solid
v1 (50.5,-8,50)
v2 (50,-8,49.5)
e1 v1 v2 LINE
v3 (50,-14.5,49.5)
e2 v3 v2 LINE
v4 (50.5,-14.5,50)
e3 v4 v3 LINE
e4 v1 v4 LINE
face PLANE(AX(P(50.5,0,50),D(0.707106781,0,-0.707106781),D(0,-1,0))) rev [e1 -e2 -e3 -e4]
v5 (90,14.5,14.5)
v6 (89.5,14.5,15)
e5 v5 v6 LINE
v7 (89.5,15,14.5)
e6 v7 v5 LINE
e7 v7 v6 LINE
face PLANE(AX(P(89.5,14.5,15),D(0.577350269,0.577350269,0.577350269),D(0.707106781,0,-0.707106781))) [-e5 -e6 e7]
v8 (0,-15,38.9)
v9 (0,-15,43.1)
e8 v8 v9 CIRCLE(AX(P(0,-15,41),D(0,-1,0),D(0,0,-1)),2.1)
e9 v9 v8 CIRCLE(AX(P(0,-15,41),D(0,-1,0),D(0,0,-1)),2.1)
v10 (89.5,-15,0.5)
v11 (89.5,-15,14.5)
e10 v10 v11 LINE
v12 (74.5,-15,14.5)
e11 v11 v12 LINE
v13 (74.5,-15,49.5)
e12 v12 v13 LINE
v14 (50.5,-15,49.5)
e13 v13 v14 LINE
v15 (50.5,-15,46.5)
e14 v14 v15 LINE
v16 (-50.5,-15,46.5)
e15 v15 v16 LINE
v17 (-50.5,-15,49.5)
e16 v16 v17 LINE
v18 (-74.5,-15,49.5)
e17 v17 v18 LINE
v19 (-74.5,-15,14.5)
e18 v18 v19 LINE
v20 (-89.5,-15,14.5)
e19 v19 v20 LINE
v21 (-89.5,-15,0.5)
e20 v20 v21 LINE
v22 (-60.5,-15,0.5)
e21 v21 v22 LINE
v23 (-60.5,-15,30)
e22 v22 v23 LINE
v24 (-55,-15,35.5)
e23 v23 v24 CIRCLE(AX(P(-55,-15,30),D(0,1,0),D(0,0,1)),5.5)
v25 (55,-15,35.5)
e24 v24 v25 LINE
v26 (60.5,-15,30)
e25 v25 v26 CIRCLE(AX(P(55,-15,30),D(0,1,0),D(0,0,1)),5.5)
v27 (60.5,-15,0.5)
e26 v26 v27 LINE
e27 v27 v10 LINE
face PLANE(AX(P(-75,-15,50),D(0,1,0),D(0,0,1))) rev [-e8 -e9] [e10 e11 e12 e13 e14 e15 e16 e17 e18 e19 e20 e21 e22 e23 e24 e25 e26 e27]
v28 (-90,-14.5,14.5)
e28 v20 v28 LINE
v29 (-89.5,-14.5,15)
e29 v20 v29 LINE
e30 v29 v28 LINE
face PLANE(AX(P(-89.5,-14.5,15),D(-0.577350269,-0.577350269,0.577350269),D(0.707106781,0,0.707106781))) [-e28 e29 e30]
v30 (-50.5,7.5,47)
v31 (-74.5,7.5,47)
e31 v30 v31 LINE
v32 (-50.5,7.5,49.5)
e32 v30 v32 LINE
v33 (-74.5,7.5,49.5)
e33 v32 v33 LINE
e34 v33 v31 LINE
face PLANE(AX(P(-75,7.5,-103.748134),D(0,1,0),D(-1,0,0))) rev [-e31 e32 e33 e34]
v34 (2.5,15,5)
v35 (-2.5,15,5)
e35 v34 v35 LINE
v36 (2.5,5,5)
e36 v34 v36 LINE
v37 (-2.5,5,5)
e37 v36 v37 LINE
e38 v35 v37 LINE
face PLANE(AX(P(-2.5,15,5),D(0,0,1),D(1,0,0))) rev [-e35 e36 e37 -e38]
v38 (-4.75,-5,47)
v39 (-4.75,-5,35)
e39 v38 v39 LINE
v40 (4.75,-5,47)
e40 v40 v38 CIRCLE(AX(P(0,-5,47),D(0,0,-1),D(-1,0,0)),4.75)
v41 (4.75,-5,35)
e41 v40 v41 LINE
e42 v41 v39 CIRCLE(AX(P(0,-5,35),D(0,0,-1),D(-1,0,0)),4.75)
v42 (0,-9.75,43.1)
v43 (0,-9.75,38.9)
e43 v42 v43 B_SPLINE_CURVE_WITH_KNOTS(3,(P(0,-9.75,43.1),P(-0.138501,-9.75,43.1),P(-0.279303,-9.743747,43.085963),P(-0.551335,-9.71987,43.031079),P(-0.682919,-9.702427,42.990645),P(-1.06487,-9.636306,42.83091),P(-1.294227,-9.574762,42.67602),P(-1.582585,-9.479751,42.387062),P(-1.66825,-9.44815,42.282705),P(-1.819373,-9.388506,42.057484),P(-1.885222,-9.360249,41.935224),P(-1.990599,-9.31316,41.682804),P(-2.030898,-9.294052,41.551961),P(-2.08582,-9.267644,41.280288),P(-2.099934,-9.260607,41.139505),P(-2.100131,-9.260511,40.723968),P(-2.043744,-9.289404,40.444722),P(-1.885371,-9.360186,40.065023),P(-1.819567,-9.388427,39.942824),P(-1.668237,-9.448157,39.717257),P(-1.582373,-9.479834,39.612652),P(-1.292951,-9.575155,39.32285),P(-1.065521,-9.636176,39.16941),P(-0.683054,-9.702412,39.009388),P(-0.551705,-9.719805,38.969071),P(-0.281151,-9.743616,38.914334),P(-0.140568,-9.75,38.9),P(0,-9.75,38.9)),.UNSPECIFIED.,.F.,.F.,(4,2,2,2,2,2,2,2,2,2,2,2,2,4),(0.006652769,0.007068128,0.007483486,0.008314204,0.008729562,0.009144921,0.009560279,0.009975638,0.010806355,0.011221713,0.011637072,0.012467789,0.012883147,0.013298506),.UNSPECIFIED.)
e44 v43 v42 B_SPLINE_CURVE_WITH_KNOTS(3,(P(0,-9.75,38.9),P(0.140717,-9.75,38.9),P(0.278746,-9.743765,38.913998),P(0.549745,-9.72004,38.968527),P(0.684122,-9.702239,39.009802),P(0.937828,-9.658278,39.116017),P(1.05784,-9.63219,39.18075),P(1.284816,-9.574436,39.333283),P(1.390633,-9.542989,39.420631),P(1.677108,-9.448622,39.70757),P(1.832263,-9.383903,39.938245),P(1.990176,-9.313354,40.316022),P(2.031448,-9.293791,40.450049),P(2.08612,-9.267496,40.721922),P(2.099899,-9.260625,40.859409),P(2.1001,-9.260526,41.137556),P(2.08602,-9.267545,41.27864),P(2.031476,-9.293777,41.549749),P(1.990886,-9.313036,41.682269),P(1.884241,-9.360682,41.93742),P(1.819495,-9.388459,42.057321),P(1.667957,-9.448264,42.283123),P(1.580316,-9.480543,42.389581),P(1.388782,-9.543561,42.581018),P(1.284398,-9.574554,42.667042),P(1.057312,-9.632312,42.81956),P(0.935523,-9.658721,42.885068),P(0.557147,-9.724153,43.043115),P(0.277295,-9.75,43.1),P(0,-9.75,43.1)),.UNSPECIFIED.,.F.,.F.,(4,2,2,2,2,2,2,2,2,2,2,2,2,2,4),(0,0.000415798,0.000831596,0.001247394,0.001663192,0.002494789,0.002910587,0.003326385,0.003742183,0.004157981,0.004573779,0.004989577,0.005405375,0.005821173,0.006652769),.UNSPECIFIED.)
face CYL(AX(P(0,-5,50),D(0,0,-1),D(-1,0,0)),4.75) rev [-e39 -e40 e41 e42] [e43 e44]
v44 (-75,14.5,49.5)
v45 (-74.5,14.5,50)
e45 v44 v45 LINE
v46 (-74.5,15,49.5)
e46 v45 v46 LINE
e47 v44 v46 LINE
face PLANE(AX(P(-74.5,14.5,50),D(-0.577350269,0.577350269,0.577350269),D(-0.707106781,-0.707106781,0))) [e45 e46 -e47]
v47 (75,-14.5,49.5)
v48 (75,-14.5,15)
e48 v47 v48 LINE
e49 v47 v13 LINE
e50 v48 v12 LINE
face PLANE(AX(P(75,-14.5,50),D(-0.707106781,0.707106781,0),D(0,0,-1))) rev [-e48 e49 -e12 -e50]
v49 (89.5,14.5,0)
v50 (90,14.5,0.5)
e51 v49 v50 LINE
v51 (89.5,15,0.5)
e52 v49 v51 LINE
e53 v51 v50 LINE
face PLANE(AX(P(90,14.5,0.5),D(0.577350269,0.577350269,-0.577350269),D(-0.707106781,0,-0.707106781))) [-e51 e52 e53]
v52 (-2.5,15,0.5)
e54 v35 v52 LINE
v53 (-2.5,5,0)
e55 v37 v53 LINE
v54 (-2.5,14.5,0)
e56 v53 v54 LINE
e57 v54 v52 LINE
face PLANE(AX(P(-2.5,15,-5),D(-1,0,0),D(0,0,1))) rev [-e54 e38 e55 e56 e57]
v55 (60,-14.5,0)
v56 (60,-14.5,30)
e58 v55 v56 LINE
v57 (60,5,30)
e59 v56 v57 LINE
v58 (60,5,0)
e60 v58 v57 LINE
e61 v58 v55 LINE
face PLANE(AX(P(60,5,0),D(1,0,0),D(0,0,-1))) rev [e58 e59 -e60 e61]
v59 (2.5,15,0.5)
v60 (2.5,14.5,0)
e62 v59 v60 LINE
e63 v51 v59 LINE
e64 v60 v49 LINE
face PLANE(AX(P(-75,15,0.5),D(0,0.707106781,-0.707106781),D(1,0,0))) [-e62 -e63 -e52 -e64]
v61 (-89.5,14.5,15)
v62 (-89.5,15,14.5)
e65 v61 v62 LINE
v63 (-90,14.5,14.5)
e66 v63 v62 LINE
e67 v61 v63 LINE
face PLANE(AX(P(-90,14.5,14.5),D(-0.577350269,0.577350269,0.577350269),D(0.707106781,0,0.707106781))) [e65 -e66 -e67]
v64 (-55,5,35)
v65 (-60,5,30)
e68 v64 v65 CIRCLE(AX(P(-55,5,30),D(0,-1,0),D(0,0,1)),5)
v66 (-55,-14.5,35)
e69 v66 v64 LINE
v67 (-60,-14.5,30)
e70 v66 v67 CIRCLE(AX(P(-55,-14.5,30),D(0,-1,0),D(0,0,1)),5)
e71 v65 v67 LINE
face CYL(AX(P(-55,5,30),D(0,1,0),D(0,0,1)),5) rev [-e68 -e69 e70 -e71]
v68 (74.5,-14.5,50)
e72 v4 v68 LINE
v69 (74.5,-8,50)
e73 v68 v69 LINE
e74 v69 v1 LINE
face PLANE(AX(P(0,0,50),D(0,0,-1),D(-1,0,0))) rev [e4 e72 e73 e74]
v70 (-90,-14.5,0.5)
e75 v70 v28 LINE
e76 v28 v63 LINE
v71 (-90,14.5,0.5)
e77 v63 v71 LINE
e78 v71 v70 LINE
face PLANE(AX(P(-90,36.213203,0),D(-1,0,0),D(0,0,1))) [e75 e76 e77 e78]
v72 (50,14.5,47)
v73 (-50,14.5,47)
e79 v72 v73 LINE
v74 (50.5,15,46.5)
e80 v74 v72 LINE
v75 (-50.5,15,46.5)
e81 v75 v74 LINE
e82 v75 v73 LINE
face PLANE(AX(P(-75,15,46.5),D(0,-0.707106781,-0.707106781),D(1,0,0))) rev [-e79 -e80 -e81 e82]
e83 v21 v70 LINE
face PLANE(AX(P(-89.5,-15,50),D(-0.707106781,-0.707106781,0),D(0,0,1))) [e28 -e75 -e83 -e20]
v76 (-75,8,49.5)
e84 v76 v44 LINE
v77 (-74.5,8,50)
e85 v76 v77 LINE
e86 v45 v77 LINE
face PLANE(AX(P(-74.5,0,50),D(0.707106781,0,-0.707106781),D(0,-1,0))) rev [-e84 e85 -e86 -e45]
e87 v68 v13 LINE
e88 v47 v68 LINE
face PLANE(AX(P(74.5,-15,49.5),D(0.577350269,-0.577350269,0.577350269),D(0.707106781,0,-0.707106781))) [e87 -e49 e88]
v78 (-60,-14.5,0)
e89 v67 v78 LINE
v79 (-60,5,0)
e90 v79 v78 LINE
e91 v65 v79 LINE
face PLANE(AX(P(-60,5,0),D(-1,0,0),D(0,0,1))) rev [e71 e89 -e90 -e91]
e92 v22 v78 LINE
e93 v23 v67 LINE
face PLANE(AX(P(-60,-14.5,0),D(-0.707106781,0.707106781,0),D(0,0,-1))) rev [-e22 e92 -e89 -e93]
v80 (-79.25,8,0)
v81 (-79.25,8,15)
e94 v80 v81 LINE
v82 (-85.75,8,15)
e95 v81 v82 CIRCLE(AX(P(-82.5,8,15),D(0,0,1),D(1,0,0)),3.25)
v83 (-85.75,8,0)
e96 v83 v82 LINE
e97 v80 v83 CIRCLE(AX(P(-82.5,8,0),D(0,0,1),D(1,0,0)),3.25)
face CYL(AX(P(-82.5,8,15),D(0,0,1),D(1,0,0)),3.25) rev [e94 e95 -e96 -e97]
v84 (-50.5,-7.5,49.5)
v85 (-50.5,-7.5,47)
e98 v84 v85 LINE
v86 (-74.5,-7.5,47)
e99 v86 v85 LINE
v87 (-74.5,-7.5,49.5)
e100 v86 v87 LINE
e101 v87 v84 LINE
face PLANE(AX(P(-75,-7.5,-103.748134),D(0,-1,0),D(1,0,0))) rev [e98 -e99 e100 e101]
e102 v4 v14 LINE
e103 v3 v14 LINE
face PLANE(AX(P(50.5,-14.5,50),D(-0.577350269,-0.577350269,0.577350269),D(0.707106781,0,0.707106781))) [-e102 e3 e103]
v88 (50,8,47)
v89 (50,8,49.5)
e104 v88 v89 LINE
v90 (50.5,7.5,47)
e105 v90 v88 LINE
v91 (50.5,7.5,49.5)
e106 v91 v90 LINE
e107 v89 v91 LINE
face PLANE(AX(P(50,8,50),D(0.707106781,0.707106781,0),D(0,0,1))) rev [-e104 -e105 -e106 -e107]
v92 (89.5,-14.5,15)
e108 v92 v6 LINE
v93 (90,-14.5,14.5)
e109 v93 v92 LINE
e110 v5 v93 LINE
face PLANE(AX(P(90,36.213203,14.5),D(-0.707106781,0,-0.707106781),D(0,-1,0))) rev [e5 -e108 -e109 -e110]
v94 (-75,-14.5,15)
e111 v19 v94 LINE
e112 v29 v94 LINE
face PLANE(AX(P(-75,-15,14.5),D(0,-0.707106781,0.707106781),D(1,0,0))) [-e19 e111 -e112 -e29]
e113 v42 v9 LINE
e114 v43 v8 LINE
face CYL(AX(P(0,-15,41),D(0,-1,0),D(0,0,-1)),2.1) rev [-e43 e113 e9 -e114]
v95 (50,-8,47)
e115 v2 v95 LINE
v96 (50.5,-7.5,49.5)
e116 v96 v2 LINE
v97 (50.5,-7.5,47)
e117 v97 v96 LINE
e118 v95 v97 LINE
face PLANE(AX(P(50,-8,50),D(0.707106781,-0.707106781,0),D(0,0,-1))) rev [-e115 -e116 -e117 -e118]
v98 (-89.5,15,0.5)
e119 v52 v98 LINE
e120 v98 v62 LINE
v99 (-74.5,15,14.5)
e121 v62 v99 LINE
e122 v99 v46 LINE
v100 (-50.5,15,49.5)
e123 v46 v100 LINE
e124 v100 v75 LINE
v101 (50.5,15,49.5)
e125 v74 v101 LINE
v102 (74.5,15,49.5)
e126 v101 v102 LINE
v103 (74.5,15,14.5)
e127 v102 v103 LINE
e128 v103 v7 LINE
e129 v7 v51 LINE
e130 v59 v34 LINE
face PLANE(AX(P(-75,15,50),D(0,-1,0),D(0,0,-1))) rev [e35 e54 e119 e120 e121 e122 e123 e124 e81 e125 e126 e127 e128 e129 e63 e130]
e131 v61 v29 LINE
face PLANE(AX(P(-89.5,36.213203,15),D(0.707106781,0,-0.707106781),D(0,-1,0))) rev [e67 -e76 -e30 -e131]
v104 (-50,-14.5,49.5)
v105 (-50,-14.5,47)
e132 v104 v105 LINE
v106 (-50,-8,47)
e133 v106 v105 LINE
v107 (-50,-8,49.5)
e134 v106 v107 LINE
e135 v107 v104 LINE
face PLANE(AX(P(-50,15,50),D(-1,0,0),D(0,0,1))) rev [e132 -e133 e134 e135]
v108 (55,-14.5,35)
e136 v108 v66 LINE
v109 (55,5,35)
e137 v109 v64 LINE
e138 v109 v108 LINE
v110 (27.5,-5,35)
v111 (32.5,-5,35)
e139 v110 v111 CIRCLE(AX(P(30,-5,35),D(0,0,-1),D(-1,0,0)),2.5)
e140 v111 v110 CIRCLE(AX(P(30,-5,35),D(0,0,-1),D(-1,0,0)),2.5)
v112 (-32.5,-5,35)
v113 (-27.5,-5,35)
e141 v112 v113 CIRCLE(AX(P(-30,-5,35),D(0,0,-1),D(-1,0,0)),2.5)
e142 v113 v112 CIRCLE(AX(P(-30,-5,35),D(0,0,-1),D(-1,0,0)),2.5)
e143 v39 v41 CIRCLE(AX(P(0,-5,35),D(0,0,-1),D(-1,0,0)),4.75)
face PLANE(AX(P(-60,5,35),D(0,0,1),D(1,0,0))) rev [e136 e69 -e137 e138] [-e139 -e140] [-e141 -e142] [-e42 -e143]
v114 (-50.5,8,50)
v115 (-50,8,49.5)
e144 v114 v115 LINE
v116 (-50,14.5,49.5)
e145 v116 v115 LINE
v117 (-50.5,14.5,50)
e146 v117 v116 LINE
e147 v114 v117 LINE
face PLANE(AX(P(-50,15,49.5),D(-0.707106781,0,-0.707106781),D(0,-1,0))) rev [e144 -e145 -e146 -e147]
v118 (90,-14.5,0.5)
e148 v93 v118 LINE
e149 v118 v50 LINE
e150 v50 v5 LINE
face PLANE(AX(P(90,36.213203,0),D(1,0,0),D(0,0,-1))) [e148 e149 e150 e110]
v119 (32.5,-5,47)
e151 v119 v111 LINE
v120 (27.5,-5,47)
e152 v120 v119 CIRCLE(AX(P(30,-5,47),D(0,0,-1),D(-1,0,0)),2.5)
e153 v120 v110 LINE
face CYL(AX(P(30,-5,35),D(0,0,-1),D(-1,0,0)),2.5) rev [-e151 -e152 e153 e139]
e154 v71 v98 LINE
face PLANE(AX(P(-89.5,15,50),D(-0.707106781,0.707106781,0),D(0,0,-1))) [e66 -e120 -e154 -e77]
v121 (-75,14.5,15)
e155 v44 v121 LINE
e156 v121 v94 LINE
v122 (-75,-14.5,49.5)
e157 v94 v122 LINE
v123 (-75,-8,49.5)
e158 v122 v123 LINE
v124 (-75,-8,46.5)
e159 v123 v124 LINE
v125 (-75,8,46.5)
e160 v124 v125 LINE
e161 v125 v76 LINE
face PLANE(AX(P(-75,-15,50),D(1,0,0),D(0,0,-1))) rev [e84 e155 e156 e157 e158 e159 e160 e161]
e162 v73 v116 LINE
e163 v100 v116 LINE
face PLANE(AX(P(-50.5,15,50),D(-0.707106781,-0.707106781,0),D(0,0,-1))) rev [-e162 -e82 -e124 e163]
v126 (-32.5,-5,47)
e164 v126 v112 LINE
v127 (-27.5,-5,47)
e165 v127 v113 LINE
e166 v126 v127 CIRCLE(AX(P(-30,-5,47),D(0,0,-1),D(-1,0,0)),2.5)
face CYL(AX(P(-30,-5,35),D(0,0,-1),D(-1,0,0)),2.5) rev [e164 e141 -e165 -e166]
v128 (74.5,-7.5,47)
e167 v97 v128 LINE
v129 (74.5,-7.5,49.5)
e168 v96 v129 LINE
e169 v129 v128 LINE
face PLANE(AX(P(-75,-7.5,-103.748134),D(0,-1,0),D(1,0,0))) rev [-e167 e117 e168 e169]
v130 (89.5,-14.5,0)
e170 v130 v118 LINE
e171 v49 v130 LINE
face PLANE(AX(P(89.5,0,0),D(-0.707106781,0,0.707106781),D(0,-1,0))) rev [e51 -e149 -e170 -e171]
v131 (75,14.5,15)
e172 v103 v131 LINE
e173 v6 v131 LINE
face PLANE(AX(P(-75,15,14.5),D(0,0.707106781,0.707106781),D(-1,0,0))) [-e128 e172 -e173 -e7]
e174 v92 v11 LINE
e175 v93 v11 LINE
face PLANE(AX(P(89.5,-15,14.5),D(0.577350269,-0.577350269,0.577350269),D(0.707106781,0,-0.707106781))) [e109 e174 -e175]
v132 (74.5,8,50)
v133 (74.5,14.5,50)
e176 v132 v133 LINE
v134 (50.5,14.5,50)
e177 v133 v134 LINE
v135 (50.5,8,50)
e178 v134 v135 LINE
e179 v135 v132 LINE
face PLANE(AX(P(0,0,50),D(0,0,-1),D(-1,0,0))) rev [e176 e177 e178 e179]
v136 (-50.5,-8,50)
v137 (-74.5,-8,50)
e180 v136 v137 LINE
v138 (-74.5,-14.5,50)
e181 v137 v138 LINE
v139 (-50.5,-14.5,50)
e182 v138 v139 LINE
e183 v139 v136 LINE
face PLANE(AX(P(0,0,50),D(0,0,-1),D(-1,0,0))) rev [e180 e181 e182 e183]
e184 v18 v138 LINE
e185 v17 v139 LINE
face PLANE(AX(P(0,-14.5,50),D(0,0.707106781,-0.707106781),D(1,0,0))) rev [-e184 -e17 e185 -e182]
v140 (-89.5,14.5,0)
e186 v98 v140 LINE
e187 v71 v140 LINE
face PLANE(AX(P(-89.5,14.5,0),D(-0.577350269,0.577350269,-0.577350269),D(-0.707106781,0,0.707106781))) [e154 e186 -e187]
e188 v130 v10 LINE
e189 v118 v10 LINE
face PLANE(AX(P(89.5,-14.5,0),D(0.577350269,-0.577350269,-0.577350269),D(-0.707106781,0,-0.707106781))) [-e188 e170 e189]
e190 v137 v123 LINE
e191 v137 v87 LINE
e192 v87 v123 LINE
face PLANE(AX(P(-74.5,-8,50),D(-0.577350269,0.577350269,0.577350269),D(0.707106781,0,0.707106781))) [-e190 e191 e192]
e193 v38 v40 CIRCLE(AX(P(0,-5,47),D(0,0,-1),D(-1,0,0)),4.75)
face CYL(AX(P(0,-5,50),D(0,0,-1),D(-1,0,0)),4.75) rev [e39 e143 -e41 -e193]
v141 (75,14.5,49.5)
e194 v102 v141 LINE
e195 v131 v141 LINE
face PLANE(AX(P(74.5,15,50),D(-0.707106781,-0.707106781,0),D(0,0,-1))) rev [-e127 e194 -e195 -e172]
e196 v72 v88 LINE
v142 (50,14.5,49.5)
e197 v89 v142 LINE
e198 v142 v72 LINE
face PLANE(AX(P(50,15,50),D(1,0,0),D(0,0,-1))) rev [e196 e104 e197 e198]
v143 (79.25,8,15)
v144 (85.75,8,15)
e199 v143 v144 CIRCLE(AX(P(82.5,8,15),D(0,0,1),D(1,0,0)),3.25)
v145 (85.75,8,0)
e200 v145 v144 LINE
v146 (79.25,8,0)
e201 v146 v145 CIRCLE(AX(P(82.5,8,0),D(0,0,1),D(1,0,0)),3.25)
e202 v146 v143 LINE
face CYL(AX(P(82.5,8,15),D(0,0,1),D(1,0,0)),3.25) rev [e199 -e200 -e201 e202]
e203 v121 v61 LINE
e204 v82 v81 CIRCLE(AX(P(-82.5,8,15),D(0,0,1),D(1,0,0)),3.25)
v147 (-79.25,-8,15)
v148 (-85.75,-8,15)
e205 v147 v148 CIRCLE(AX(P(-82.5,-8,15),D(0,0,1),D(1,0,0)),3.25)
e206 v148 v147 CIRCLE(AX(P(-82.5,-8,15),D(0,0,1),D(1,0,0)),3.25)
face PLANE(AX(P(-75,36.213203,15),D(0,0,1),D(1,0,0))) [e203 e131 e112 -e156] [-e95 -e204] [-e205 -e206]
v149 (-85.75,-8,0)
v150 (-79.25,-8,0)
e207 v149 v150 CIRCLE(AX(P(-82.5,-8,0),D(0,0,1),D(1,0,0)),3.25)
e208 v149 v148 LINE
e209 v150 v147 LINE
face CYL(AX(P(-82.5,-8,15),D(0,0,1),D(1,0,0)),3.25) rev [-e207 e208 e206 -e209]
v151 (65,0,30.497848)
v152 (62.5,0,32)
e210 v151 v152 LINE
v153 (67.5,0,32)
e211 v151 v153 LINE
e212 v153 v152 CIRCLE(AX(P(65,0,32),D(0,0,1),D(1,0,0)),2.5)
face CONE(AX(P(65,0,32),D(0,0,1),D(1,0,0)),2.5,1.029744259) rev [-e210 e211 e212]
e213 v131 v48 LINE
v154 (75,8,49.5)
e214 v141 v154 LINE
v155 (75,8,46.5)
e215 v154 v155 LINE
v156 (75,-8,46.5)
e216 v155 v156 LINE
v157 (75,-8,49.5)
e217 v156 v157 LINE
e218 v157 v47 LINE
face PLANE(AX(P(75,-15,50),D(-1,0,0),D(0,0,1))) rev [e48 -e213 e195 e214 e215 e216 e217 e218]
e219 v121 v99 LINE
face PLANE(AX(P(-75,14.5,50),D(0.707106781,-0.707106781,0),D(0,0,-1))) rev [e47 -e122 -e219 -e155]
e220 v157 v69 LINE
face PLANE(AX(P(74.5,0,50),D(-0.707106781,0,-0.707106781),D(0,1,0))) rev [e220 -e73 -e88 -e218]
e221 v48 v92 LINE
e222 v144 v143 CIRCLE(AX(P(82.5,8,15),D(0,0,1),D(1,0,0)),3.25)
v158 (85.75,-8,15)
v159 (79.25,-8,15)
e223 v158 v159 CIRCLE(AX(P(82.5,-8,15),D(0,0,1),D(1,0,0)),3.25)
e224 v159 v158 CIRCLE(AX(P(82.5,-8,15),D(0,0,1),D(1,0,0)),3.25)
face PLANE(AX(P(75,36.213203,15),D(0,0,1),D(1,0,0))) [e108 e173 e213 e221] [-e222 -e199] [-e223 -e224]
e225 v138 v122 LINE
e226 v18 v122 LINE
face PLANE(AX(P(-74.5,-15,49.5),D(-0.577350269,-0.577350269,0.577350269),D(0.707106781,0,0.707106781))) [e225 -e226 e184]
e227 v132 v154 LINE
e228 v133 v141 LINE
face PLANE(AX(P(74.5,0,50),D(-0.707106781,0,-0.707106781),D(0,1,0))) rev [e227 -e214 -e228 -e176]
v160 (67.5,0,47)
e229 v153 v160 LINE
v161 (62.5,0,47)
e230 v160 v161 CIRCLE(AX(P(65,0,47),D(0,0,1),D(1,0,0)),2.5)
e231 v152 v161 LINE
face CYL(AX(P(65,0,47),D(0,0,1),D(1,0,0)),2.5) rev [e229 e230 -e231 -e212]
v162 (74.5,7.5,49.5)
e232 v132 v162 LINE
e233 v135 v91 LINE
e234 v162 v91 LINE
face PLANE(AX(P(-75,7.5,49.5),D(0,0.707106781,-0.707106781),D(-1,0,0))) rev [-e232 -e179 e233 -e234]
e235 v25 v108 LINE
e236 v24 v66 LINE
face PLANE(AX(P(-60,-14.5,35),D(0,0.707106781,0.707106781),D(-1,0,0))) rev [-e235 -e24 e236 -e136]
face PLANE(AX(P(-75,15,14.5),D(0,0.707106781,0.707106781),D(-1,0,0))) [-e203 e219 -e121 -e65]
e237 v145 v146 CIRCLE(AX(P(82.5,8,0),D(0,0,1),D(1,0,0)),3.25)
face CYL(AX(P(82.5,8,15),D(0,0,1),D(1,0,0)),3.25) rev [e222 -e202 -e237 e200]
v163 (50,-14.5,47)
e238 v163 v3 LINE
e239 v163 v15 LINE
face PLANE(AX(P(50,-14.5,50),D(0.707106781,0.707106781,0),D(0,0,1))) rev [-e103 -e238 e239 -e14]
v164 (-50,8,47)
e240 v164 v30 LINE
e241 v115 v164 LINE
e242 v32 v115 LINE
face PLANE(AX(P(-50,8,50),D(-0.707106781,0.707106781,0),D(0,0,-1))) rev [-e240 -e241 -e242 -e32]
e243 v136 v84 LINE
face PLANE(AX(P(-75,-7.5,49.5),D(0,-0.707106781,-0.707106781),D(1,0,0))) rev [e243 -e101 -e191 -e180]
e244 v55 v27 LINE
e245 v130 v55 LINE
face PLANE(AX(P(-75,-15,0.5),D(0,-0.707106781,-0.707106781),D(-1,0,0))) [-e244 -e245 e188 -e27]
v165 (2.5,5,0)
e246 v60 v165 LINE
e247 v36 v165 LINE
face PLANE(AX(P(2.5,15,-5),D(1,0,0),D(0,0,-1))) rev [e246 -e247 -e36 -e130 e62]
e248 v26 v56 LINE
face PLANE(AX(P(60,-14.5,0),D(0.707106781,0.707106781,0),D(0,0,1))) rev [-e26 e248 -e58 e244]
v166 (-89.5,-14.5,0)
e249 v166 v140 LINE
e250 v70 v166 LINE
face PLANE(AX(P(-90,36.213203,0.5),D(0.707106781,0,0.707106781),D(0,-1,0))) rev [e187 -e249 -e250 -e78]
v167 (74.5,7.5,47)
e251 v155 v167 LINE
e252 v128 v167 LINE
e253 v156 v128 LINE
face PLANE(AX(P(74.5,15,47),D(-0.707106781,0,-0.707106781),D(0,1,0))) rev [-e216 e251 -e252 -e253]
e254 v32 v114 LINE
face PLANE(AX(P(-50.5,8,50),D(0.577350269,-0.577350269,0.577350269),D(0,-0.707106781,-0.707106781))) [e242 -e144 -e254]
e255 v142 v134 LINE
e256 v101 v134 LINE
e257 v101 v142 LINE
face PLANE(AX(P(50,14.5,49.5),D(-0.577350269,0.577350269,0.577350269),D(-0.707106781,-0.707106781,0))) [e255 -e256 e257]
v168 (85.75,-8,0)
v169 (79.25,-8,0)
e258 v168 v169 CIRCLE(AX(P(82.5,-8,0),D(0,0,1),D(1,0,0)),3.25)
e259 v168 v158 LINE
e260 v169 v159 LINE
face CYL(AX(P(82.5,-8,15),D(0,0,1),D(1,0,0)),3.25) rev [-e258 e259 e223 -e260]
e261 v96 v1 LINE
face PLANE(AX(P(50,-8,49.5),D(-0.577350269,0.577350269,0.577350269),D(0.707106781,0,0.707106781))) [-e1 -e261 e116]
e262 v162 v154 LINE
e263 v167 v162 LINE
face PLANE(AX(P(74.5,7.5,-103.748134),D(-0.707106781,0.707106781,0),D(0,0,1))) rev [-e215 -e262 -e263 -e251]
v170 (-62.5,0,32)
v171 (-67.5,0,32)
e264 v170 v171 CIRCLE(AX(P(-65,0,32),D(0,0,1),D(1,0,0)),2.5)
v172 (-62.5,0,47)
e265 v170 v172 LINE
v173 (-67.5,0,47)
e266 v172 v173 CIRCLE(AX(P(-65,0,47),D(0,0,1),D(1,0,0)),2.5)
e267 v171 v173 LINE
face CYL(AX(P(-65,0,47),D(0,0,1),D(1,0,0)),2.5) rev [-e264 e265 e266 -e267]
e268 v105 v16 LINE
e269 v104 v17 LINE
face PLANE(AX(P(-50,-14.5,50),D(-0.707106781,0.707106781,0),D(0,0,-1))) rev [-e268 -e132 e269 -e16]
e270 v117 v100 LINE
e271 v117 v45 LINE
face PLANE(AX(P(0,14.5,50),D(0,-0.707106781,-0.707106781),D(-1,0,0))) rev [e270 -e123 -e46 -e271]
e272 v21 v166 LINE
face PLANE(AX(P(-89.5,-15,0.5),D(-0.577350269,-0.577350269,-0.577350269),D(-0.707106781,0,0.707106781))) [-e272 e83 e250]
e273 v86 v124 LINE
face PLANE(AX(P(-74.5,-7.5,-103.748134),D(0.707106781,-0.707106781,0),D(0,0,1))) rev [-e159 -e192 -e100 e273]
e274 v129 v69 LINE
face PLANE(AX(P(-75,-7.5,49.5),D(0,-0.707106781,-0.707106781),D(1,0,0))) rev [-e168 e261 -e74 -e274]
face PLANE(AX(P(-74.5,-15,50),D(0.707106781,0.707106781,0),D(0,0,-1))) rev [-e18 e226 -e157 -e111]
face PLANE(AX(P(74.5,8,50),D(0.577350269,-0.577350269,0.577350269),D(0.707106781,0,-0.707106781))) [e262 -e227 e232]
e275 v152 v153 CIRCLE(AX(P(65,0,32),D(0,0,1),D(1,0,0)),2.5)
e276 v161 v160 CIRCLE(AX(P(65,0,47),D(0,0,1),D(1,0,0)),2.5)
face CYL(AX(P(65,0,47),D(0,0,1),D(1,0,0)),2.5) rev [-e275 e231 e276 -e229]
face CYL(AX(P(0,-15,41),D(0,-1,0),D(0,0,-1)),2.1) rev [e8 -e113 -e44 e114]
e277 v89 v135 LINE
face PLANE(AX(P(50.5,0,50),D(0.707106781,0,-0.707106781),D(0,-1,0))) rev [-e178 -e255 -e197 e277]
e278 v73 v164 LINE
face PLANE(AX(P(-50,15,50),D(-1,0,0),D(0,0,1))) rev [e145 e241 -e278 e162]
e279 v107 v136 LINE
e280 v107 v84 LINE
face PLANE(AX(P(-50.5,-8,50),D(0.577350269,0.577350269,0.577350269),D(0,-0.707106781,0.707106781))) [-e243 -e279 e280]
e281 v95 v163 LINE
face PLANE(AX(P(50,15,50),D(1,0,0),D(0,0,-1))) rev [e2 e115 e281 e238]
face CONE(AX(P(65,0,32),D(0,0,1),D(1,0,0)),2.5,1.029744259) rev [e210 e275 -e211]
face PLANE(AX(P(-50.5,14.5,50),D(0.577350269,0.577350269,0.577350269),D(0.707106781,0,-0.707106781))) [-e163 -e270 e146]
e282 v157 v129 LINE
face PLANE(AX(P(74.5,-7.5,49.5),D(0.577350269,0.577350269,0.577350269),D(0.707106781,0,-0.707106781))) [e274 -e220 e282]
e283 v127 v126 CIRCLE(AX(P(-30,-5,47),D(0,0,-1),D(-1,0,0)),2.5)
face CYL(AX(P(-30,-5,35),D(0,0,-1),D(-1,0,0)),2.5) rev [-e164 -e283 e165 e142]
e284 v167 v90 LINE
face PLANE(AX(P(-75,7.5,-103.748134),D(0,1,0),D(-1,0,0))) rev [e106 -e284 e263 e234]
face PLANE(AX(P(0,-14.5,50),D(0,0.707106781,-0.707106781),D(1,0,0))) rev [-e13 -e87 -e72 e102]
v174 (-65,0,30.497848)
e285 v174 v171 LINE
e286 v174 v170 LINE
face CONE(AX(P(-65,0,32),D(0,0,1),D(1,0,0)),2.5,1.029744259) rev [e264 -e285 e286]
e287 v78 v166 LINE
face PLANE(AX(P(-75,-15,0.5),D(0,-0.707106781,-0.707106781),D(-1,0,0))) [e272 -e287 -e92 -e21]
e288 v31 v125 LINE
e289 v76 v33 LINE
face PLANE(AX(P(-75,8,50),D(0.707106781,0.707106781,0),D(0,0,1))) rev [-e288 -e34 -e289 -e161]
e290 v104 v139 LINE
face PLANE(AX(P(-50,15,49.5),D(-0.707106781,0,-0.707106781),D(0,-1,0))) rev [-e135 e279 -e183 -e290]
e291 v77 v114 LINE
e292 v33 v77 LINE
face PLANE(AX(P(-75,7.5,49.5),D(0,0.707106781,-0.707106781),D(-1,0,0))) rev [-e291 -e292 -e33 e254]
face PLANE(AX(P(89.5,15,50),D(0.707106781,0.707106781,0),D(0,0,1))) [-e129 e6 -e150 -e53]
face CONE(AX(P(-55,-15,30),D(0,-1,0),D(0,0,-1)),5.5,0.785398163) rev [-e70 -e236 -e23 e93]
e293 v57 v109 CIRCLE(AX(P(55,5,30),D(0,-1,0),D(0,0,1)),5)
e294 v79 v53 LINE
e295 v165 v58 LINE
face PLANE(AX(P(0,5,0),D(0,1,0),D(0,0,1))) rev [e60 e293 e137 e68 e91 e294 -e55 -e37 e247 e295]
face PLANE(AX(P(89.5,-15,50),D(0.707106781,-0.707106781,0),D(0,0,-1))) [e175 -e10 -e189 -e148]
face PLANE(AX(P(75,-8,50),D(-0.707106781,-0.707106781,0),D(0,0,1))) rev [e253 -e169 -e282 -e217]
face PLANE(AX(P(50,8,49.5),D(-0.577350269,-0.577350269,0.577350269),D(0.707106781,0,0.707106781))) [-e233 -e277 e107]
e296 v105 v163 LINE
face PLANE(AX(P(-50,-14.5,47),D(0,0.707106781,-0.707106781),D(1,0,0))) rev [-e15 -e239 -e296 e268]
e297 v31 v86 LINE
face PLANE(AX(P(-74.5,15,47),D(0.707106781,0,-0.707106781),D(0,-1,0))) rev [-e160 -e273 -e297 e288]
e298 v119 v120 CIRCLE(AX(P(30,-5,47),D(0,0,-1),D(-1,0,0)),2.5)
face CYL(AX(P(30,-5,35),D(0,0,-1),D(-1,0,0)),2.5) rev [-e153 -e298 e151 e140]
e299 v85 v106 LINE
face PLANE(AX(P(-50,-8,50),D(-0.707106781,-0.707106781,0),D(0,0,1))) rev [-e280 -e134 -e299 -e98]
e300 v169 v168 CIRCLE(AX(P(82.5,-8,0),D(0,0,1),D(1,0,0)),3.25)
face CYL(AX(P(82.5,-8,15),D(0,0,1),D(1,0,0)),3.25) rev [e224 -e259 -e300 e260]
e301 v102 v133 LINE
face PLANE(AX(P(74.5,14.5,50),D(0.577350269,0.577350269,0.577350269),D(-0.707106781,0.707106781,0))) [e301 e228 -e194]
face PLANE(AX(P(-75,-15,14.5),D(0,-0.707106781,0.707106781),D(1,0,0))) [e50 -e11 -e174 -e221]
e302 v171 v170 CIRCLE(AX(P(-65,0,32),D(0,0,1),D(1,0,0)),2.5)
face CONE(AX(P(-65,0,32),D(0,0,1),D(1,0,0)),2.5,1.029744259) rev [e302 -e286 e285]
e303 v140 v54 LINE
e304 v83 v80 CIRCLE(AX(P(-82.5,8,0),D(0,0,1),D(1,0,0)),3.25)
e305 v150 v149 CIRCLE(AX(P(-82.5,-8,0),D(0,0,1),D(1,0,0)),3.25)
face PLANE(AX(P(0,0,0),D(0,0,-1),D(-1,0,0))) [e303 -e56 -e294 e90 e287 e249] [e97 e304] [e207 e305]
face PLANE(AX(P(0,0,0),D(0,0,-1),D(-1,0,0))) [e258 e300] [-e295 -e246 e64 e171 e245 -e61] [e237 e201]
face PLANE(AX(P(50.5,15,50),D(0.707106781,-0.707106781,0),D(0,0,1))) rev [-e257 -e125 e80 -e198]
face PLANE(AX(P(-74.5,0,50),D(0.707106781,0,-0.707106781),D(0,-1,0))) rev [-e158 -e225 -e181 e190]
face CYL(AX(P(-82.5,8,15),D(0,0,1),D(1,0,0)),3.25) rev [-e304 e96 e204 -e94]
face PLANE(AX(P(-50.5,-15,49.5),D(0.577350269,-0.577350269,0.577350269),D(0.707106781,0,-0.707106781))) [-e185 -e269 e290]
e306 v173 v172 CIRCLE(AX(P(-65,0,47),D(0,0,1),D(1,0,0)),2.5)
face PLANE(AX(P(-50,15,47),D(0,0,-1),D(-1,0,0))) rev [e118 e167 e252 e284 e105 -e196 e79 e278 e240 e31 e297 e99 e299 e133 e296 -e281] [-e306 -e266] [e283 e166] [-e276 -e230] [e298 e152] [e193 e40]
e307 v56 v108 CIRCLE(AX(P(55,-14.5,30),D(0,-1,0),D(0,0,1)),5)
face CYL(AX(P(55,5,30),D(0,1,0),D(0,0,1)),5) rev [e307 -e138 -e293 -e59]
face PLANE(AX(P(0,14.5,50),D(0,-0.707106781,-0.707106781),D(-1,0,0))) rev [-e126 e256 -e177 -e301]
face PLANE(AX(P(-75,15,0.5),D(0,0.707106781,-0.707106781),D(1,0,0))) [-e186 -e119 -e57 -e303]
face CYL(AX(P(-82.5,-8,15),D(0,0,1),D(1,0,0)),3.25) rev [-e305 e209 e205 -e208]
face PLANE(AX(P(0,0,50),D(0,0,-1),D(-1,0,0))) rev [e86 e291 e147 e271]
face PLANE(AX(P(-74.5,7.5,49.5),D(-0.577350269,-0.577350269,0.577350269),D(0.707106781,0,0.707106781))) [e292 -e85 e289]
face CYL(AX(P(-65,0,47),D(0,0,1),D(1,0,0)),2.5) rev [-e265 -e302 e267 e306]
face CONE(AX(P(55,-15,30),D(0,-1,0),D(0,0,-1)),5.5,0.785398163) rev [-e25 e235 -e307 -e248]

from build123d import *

# Parameters (mm, degrees)
SKETCH_1_W              = 150
SKETCH_1_H              = 30
EXTRUDE_1_DEPTH         = 50
SKETCH_3_W              = 120
SKETCH_3_H              = 35
CUT_EXTRUDE_2_DEPTH     = 20
SKETCH_4_W              = 100
SKETCH_4_H              = 3
CUT_EXTRUDE_3_DEPTH     = 96
SKETCH_5_W              = 150
SKETCH_5_H              = 15
CUT_EXTRUDE_4_DEPTH     = 3
FILLET_1_R              = 5
HOLE_WIZARD_M6_1_D      = 5
SKETCH_11_R             = 4.75
CUT_EXTRUDE_6_DEPTH     = 85.113019206
HOLE_WIZARD_M5_1_REACH  = 97
HOLE_WIZARD_M5_1_BORE_R = 2.1
HOLE_WIZARD_M6_2_D      = 5
HOLE_WIZARD_M6_2_DEPTH  = 15
HOLE_WIZARD_M6_2_TIP    = 1.502151548
SKETCH_18_W             = 15
SKETCH_18_H             = 15
EXTRUDE_2_DEPTH         = 30
HOLE_WIZARD_6_5_6_5_1_D = 6.5
SKETCH_21_W             = 5
SKETCH_21_H             = 10
CUT_EXTRUDE_7_DEPTH     = 105.880884836
CHAMFER_1_SIZE          = 0.5


with BuildPart() as part:
    # 草图1 → 凸台-拉伸1 (new body)
    with BuildSketch(Plane.XY):
        Rectangle(SKETCH_1_W, SKETCH_1_H)
    extrude(amount=EXTRUDE_1_DEPTH)

    # 草图3 → 切除-拉伸2 (cut)
    with BuildSketch(Plane.XZ.offset(15)):
        with Locations((0, 17.5)):
            Rectangle(SKETCH_3_W, SKETCH_3_H)
    extrude(amount=-CUT_EXTRUDE_2_DEPTH, mode=Mode.SUBTRACT)

    # 草图4 → 切除-拉伸3 (cut, through all)
    with BuildSketch(Plane.XZ.offset(15)):
        with Locations((0, 48.5)):
            Rectangle(SKETCH_4_W, SKETCH_4_H)
    extrude(amount=-CUT_EXTRUDE_3_DEPTH, mode=Mode.SUBTRACT)

    # 草图5 → 切除-拉伸4 (cut)
    with BuildSketch(Plane.XY.offset(50)):
        Rectangle(SKETCH_5_W, SKETCH_5_H)
    extrude(amount=-CUT_EXTRUDE_4_DEPTH, mode=Mode.SUBTRACT)

    # 圆角1
    fillet_1_edges = [part.edges().sort_by_distance(p)[0] for p in [
        (-60, -5, 35),
        (60, -5, 35),
    ]]
    fillet(fillet_1_edges, radius=FILLET_1_R)

    # M6 螺纹孔1 (through all)
    with Locations(Plane(origin=(0, 0, 35), x_dir=(-1, 0, 0), z_dir=(0, 0, -1))):
        with Locations((30, -5), (-30, -5)):
            Hole(HOLE_WIZARD_M6_1_D / 2)

    # 草图11 → 切除-拉伸6 (cut, through all)
    with BuildSketch(Plane(origin=(0, 0, 35), x_dir=(-1, 0, 0), z_dir=(0, 0, -1))):
        with Locations((0, -5)):
            Circle(SKETCH_11_R)
    extrude(amount=-CUT_EXTRUDE_6_DEPTH, mode=Mode.SUBTRACT)

    # M5 螺纹孔1 bore → M5 螺纹孔1 (cut, up to next)
    with BuildSketch(Plane(origin=(0, -15, 0), x_dir=(-1, 0, 0), z_dir=(0, -1, 0)), mode=Mode.PRIVATE) as hole_wizard_m5_1_sk1:
        with Locations((0, -41)):
            Circle(HOLE_WIZARD_M5_1_BORE_R)
    hole_wizard_m5_1_tool1 = extrude(hole_wizard_m5_1_sk1.sketch, amount=-HOLE_WIZARD_M5_1_REACH, mode=Mode.PRIVATE) & part.part
    add(hole_wizard_m5_1_tool1.solids().sort_by_distance((0, -15, 41))[0], mode=Mode.SUBTRACT)

    # M6 螺纹孔2
    with Locations(Plane.XY.offset(47)):
        with Locations((-65, 0), (65, 0)):
            Hole(HOLE_WIZARD_M6_2_D / 2, depth=HOLE_WIZARD_M6_2_DEPTH)
            with Locations((0, 0, -(HOLE_WIZARD_M6_2_DEPTH + HOLE_WIZARD_M6_2_TIP / 2))):  # 118° drill point
                Cone(0, HOLE_WIZARD_M6_2_D / 2, HOLE_WIZARD_M6_2_TIP, mode=Mode.SUBTRACT)

    # 草图18 → 凸台-拉伸2 (add)
    with BuildSketch(Plane.XZ.offset(15)):
        with Locations((-82.5, 7.5)):
            Rectangle(SKETCH_18_W, SKETCH_18_H)
        with Locations((82.5, 7.5)):
            Rectangle(SKETCH_18_W, SKETCH_18_H)
    extrude(amount=-EXTRUDE_2_DEPTH)

    # Ø6.5 (6.5) 直径孔1 (through all)
    with Locations(Plane.XY.offset(15)):
        with Locations((-82.5, 8), (-82.5, -8), (82.5, -8), (82.5, 8)):
            Hole(HOLE_WIZARD_6_5_6_5_1_D / 2)

    # 草图21 → 切除-拉伸7 (cut, through all)
    with BuildSketch(Plane.XZ.offset(-5)):
        Rectangle(SKETCH_21_W, SKETCH_21_H)
    extrude(amount=-CUT_EXTRUDE_7_DEPTH, mode=Mode.SUBTRACT)

    # 倒角1
    chamfer_1_edges = [part.edges().sort_by_distance(p)[0] for p in [
        (-90, 0, 0),
        (-90, 0, 15),
        (-82.5, -15, 15),
        (-90, -15, 7.5),
        (-90, 15, 7.5),
        (-82.5, 15, 15),
        (-75, 11.25, 50),
        (90, 0, 0),
        (90, 0, 15),
        (90, -15, 7.5),
        (82.5, -15, 15),
        (82.5, 15, 15),
        (90, 15, 7.5),
        (75, -15, 0),
        (-62.5, -15, 50),
        (-46.25, 15, 0),
        (60, -15, 15),
        (-62.5, 15, 50),
        (62.5, -15, 50),
        (-50, 15, 48.5),
        (-50, 11.25, 50),
        (50, 15, 48.5),
        (50, 11.25, 50),
        (0, 15, 47),
        (-50, -15, 48.5),
        (0, -15, 47),
        (50, -15, 48.5),
        (50, -11.25, 50),
        (-50, -11.25, 50),
        (75, -11.25, 50),
        (-75, -15, 0),
        (75, 11.25, 50),
        (-75, -11.25, 50),
        (-62.5, 7.5, 50),
        (-62.5, -7.5, 50),
        (62.5, -7.5, 50),
        (62.5, 7.5, 50),
        (-50, -7.5, 48.5),
        (50, -7.5, 48.5),
        (75, -7.5, 48.5),
        (46.25, 15, 0),
        (-50, 7.5, 48.5),
        (-75, 7.5, 48.5),
        (50, 7.5, 48.5),
        (75, 0, 47),
        (75, 7.5, 48.5),
        (-75, 0, 47),
        (-75, -7.5, 48.5),
        (-60, -15, 15),
        (0, -15, 35),
        (75, -15, 32.5),
        (-75, -15, 32.5),
        (-75, 15, 32.5),
        (-58.535533906, -15, 33.535533906),
        (58.535533906, -15, 33.535533906),
        (75, 15, 32.5),
        (62.5, 15, 50),
    ]]
    chamfer(chamfer_1_edges, length=CHAMFER_1_SIZE)


solid = part.part
